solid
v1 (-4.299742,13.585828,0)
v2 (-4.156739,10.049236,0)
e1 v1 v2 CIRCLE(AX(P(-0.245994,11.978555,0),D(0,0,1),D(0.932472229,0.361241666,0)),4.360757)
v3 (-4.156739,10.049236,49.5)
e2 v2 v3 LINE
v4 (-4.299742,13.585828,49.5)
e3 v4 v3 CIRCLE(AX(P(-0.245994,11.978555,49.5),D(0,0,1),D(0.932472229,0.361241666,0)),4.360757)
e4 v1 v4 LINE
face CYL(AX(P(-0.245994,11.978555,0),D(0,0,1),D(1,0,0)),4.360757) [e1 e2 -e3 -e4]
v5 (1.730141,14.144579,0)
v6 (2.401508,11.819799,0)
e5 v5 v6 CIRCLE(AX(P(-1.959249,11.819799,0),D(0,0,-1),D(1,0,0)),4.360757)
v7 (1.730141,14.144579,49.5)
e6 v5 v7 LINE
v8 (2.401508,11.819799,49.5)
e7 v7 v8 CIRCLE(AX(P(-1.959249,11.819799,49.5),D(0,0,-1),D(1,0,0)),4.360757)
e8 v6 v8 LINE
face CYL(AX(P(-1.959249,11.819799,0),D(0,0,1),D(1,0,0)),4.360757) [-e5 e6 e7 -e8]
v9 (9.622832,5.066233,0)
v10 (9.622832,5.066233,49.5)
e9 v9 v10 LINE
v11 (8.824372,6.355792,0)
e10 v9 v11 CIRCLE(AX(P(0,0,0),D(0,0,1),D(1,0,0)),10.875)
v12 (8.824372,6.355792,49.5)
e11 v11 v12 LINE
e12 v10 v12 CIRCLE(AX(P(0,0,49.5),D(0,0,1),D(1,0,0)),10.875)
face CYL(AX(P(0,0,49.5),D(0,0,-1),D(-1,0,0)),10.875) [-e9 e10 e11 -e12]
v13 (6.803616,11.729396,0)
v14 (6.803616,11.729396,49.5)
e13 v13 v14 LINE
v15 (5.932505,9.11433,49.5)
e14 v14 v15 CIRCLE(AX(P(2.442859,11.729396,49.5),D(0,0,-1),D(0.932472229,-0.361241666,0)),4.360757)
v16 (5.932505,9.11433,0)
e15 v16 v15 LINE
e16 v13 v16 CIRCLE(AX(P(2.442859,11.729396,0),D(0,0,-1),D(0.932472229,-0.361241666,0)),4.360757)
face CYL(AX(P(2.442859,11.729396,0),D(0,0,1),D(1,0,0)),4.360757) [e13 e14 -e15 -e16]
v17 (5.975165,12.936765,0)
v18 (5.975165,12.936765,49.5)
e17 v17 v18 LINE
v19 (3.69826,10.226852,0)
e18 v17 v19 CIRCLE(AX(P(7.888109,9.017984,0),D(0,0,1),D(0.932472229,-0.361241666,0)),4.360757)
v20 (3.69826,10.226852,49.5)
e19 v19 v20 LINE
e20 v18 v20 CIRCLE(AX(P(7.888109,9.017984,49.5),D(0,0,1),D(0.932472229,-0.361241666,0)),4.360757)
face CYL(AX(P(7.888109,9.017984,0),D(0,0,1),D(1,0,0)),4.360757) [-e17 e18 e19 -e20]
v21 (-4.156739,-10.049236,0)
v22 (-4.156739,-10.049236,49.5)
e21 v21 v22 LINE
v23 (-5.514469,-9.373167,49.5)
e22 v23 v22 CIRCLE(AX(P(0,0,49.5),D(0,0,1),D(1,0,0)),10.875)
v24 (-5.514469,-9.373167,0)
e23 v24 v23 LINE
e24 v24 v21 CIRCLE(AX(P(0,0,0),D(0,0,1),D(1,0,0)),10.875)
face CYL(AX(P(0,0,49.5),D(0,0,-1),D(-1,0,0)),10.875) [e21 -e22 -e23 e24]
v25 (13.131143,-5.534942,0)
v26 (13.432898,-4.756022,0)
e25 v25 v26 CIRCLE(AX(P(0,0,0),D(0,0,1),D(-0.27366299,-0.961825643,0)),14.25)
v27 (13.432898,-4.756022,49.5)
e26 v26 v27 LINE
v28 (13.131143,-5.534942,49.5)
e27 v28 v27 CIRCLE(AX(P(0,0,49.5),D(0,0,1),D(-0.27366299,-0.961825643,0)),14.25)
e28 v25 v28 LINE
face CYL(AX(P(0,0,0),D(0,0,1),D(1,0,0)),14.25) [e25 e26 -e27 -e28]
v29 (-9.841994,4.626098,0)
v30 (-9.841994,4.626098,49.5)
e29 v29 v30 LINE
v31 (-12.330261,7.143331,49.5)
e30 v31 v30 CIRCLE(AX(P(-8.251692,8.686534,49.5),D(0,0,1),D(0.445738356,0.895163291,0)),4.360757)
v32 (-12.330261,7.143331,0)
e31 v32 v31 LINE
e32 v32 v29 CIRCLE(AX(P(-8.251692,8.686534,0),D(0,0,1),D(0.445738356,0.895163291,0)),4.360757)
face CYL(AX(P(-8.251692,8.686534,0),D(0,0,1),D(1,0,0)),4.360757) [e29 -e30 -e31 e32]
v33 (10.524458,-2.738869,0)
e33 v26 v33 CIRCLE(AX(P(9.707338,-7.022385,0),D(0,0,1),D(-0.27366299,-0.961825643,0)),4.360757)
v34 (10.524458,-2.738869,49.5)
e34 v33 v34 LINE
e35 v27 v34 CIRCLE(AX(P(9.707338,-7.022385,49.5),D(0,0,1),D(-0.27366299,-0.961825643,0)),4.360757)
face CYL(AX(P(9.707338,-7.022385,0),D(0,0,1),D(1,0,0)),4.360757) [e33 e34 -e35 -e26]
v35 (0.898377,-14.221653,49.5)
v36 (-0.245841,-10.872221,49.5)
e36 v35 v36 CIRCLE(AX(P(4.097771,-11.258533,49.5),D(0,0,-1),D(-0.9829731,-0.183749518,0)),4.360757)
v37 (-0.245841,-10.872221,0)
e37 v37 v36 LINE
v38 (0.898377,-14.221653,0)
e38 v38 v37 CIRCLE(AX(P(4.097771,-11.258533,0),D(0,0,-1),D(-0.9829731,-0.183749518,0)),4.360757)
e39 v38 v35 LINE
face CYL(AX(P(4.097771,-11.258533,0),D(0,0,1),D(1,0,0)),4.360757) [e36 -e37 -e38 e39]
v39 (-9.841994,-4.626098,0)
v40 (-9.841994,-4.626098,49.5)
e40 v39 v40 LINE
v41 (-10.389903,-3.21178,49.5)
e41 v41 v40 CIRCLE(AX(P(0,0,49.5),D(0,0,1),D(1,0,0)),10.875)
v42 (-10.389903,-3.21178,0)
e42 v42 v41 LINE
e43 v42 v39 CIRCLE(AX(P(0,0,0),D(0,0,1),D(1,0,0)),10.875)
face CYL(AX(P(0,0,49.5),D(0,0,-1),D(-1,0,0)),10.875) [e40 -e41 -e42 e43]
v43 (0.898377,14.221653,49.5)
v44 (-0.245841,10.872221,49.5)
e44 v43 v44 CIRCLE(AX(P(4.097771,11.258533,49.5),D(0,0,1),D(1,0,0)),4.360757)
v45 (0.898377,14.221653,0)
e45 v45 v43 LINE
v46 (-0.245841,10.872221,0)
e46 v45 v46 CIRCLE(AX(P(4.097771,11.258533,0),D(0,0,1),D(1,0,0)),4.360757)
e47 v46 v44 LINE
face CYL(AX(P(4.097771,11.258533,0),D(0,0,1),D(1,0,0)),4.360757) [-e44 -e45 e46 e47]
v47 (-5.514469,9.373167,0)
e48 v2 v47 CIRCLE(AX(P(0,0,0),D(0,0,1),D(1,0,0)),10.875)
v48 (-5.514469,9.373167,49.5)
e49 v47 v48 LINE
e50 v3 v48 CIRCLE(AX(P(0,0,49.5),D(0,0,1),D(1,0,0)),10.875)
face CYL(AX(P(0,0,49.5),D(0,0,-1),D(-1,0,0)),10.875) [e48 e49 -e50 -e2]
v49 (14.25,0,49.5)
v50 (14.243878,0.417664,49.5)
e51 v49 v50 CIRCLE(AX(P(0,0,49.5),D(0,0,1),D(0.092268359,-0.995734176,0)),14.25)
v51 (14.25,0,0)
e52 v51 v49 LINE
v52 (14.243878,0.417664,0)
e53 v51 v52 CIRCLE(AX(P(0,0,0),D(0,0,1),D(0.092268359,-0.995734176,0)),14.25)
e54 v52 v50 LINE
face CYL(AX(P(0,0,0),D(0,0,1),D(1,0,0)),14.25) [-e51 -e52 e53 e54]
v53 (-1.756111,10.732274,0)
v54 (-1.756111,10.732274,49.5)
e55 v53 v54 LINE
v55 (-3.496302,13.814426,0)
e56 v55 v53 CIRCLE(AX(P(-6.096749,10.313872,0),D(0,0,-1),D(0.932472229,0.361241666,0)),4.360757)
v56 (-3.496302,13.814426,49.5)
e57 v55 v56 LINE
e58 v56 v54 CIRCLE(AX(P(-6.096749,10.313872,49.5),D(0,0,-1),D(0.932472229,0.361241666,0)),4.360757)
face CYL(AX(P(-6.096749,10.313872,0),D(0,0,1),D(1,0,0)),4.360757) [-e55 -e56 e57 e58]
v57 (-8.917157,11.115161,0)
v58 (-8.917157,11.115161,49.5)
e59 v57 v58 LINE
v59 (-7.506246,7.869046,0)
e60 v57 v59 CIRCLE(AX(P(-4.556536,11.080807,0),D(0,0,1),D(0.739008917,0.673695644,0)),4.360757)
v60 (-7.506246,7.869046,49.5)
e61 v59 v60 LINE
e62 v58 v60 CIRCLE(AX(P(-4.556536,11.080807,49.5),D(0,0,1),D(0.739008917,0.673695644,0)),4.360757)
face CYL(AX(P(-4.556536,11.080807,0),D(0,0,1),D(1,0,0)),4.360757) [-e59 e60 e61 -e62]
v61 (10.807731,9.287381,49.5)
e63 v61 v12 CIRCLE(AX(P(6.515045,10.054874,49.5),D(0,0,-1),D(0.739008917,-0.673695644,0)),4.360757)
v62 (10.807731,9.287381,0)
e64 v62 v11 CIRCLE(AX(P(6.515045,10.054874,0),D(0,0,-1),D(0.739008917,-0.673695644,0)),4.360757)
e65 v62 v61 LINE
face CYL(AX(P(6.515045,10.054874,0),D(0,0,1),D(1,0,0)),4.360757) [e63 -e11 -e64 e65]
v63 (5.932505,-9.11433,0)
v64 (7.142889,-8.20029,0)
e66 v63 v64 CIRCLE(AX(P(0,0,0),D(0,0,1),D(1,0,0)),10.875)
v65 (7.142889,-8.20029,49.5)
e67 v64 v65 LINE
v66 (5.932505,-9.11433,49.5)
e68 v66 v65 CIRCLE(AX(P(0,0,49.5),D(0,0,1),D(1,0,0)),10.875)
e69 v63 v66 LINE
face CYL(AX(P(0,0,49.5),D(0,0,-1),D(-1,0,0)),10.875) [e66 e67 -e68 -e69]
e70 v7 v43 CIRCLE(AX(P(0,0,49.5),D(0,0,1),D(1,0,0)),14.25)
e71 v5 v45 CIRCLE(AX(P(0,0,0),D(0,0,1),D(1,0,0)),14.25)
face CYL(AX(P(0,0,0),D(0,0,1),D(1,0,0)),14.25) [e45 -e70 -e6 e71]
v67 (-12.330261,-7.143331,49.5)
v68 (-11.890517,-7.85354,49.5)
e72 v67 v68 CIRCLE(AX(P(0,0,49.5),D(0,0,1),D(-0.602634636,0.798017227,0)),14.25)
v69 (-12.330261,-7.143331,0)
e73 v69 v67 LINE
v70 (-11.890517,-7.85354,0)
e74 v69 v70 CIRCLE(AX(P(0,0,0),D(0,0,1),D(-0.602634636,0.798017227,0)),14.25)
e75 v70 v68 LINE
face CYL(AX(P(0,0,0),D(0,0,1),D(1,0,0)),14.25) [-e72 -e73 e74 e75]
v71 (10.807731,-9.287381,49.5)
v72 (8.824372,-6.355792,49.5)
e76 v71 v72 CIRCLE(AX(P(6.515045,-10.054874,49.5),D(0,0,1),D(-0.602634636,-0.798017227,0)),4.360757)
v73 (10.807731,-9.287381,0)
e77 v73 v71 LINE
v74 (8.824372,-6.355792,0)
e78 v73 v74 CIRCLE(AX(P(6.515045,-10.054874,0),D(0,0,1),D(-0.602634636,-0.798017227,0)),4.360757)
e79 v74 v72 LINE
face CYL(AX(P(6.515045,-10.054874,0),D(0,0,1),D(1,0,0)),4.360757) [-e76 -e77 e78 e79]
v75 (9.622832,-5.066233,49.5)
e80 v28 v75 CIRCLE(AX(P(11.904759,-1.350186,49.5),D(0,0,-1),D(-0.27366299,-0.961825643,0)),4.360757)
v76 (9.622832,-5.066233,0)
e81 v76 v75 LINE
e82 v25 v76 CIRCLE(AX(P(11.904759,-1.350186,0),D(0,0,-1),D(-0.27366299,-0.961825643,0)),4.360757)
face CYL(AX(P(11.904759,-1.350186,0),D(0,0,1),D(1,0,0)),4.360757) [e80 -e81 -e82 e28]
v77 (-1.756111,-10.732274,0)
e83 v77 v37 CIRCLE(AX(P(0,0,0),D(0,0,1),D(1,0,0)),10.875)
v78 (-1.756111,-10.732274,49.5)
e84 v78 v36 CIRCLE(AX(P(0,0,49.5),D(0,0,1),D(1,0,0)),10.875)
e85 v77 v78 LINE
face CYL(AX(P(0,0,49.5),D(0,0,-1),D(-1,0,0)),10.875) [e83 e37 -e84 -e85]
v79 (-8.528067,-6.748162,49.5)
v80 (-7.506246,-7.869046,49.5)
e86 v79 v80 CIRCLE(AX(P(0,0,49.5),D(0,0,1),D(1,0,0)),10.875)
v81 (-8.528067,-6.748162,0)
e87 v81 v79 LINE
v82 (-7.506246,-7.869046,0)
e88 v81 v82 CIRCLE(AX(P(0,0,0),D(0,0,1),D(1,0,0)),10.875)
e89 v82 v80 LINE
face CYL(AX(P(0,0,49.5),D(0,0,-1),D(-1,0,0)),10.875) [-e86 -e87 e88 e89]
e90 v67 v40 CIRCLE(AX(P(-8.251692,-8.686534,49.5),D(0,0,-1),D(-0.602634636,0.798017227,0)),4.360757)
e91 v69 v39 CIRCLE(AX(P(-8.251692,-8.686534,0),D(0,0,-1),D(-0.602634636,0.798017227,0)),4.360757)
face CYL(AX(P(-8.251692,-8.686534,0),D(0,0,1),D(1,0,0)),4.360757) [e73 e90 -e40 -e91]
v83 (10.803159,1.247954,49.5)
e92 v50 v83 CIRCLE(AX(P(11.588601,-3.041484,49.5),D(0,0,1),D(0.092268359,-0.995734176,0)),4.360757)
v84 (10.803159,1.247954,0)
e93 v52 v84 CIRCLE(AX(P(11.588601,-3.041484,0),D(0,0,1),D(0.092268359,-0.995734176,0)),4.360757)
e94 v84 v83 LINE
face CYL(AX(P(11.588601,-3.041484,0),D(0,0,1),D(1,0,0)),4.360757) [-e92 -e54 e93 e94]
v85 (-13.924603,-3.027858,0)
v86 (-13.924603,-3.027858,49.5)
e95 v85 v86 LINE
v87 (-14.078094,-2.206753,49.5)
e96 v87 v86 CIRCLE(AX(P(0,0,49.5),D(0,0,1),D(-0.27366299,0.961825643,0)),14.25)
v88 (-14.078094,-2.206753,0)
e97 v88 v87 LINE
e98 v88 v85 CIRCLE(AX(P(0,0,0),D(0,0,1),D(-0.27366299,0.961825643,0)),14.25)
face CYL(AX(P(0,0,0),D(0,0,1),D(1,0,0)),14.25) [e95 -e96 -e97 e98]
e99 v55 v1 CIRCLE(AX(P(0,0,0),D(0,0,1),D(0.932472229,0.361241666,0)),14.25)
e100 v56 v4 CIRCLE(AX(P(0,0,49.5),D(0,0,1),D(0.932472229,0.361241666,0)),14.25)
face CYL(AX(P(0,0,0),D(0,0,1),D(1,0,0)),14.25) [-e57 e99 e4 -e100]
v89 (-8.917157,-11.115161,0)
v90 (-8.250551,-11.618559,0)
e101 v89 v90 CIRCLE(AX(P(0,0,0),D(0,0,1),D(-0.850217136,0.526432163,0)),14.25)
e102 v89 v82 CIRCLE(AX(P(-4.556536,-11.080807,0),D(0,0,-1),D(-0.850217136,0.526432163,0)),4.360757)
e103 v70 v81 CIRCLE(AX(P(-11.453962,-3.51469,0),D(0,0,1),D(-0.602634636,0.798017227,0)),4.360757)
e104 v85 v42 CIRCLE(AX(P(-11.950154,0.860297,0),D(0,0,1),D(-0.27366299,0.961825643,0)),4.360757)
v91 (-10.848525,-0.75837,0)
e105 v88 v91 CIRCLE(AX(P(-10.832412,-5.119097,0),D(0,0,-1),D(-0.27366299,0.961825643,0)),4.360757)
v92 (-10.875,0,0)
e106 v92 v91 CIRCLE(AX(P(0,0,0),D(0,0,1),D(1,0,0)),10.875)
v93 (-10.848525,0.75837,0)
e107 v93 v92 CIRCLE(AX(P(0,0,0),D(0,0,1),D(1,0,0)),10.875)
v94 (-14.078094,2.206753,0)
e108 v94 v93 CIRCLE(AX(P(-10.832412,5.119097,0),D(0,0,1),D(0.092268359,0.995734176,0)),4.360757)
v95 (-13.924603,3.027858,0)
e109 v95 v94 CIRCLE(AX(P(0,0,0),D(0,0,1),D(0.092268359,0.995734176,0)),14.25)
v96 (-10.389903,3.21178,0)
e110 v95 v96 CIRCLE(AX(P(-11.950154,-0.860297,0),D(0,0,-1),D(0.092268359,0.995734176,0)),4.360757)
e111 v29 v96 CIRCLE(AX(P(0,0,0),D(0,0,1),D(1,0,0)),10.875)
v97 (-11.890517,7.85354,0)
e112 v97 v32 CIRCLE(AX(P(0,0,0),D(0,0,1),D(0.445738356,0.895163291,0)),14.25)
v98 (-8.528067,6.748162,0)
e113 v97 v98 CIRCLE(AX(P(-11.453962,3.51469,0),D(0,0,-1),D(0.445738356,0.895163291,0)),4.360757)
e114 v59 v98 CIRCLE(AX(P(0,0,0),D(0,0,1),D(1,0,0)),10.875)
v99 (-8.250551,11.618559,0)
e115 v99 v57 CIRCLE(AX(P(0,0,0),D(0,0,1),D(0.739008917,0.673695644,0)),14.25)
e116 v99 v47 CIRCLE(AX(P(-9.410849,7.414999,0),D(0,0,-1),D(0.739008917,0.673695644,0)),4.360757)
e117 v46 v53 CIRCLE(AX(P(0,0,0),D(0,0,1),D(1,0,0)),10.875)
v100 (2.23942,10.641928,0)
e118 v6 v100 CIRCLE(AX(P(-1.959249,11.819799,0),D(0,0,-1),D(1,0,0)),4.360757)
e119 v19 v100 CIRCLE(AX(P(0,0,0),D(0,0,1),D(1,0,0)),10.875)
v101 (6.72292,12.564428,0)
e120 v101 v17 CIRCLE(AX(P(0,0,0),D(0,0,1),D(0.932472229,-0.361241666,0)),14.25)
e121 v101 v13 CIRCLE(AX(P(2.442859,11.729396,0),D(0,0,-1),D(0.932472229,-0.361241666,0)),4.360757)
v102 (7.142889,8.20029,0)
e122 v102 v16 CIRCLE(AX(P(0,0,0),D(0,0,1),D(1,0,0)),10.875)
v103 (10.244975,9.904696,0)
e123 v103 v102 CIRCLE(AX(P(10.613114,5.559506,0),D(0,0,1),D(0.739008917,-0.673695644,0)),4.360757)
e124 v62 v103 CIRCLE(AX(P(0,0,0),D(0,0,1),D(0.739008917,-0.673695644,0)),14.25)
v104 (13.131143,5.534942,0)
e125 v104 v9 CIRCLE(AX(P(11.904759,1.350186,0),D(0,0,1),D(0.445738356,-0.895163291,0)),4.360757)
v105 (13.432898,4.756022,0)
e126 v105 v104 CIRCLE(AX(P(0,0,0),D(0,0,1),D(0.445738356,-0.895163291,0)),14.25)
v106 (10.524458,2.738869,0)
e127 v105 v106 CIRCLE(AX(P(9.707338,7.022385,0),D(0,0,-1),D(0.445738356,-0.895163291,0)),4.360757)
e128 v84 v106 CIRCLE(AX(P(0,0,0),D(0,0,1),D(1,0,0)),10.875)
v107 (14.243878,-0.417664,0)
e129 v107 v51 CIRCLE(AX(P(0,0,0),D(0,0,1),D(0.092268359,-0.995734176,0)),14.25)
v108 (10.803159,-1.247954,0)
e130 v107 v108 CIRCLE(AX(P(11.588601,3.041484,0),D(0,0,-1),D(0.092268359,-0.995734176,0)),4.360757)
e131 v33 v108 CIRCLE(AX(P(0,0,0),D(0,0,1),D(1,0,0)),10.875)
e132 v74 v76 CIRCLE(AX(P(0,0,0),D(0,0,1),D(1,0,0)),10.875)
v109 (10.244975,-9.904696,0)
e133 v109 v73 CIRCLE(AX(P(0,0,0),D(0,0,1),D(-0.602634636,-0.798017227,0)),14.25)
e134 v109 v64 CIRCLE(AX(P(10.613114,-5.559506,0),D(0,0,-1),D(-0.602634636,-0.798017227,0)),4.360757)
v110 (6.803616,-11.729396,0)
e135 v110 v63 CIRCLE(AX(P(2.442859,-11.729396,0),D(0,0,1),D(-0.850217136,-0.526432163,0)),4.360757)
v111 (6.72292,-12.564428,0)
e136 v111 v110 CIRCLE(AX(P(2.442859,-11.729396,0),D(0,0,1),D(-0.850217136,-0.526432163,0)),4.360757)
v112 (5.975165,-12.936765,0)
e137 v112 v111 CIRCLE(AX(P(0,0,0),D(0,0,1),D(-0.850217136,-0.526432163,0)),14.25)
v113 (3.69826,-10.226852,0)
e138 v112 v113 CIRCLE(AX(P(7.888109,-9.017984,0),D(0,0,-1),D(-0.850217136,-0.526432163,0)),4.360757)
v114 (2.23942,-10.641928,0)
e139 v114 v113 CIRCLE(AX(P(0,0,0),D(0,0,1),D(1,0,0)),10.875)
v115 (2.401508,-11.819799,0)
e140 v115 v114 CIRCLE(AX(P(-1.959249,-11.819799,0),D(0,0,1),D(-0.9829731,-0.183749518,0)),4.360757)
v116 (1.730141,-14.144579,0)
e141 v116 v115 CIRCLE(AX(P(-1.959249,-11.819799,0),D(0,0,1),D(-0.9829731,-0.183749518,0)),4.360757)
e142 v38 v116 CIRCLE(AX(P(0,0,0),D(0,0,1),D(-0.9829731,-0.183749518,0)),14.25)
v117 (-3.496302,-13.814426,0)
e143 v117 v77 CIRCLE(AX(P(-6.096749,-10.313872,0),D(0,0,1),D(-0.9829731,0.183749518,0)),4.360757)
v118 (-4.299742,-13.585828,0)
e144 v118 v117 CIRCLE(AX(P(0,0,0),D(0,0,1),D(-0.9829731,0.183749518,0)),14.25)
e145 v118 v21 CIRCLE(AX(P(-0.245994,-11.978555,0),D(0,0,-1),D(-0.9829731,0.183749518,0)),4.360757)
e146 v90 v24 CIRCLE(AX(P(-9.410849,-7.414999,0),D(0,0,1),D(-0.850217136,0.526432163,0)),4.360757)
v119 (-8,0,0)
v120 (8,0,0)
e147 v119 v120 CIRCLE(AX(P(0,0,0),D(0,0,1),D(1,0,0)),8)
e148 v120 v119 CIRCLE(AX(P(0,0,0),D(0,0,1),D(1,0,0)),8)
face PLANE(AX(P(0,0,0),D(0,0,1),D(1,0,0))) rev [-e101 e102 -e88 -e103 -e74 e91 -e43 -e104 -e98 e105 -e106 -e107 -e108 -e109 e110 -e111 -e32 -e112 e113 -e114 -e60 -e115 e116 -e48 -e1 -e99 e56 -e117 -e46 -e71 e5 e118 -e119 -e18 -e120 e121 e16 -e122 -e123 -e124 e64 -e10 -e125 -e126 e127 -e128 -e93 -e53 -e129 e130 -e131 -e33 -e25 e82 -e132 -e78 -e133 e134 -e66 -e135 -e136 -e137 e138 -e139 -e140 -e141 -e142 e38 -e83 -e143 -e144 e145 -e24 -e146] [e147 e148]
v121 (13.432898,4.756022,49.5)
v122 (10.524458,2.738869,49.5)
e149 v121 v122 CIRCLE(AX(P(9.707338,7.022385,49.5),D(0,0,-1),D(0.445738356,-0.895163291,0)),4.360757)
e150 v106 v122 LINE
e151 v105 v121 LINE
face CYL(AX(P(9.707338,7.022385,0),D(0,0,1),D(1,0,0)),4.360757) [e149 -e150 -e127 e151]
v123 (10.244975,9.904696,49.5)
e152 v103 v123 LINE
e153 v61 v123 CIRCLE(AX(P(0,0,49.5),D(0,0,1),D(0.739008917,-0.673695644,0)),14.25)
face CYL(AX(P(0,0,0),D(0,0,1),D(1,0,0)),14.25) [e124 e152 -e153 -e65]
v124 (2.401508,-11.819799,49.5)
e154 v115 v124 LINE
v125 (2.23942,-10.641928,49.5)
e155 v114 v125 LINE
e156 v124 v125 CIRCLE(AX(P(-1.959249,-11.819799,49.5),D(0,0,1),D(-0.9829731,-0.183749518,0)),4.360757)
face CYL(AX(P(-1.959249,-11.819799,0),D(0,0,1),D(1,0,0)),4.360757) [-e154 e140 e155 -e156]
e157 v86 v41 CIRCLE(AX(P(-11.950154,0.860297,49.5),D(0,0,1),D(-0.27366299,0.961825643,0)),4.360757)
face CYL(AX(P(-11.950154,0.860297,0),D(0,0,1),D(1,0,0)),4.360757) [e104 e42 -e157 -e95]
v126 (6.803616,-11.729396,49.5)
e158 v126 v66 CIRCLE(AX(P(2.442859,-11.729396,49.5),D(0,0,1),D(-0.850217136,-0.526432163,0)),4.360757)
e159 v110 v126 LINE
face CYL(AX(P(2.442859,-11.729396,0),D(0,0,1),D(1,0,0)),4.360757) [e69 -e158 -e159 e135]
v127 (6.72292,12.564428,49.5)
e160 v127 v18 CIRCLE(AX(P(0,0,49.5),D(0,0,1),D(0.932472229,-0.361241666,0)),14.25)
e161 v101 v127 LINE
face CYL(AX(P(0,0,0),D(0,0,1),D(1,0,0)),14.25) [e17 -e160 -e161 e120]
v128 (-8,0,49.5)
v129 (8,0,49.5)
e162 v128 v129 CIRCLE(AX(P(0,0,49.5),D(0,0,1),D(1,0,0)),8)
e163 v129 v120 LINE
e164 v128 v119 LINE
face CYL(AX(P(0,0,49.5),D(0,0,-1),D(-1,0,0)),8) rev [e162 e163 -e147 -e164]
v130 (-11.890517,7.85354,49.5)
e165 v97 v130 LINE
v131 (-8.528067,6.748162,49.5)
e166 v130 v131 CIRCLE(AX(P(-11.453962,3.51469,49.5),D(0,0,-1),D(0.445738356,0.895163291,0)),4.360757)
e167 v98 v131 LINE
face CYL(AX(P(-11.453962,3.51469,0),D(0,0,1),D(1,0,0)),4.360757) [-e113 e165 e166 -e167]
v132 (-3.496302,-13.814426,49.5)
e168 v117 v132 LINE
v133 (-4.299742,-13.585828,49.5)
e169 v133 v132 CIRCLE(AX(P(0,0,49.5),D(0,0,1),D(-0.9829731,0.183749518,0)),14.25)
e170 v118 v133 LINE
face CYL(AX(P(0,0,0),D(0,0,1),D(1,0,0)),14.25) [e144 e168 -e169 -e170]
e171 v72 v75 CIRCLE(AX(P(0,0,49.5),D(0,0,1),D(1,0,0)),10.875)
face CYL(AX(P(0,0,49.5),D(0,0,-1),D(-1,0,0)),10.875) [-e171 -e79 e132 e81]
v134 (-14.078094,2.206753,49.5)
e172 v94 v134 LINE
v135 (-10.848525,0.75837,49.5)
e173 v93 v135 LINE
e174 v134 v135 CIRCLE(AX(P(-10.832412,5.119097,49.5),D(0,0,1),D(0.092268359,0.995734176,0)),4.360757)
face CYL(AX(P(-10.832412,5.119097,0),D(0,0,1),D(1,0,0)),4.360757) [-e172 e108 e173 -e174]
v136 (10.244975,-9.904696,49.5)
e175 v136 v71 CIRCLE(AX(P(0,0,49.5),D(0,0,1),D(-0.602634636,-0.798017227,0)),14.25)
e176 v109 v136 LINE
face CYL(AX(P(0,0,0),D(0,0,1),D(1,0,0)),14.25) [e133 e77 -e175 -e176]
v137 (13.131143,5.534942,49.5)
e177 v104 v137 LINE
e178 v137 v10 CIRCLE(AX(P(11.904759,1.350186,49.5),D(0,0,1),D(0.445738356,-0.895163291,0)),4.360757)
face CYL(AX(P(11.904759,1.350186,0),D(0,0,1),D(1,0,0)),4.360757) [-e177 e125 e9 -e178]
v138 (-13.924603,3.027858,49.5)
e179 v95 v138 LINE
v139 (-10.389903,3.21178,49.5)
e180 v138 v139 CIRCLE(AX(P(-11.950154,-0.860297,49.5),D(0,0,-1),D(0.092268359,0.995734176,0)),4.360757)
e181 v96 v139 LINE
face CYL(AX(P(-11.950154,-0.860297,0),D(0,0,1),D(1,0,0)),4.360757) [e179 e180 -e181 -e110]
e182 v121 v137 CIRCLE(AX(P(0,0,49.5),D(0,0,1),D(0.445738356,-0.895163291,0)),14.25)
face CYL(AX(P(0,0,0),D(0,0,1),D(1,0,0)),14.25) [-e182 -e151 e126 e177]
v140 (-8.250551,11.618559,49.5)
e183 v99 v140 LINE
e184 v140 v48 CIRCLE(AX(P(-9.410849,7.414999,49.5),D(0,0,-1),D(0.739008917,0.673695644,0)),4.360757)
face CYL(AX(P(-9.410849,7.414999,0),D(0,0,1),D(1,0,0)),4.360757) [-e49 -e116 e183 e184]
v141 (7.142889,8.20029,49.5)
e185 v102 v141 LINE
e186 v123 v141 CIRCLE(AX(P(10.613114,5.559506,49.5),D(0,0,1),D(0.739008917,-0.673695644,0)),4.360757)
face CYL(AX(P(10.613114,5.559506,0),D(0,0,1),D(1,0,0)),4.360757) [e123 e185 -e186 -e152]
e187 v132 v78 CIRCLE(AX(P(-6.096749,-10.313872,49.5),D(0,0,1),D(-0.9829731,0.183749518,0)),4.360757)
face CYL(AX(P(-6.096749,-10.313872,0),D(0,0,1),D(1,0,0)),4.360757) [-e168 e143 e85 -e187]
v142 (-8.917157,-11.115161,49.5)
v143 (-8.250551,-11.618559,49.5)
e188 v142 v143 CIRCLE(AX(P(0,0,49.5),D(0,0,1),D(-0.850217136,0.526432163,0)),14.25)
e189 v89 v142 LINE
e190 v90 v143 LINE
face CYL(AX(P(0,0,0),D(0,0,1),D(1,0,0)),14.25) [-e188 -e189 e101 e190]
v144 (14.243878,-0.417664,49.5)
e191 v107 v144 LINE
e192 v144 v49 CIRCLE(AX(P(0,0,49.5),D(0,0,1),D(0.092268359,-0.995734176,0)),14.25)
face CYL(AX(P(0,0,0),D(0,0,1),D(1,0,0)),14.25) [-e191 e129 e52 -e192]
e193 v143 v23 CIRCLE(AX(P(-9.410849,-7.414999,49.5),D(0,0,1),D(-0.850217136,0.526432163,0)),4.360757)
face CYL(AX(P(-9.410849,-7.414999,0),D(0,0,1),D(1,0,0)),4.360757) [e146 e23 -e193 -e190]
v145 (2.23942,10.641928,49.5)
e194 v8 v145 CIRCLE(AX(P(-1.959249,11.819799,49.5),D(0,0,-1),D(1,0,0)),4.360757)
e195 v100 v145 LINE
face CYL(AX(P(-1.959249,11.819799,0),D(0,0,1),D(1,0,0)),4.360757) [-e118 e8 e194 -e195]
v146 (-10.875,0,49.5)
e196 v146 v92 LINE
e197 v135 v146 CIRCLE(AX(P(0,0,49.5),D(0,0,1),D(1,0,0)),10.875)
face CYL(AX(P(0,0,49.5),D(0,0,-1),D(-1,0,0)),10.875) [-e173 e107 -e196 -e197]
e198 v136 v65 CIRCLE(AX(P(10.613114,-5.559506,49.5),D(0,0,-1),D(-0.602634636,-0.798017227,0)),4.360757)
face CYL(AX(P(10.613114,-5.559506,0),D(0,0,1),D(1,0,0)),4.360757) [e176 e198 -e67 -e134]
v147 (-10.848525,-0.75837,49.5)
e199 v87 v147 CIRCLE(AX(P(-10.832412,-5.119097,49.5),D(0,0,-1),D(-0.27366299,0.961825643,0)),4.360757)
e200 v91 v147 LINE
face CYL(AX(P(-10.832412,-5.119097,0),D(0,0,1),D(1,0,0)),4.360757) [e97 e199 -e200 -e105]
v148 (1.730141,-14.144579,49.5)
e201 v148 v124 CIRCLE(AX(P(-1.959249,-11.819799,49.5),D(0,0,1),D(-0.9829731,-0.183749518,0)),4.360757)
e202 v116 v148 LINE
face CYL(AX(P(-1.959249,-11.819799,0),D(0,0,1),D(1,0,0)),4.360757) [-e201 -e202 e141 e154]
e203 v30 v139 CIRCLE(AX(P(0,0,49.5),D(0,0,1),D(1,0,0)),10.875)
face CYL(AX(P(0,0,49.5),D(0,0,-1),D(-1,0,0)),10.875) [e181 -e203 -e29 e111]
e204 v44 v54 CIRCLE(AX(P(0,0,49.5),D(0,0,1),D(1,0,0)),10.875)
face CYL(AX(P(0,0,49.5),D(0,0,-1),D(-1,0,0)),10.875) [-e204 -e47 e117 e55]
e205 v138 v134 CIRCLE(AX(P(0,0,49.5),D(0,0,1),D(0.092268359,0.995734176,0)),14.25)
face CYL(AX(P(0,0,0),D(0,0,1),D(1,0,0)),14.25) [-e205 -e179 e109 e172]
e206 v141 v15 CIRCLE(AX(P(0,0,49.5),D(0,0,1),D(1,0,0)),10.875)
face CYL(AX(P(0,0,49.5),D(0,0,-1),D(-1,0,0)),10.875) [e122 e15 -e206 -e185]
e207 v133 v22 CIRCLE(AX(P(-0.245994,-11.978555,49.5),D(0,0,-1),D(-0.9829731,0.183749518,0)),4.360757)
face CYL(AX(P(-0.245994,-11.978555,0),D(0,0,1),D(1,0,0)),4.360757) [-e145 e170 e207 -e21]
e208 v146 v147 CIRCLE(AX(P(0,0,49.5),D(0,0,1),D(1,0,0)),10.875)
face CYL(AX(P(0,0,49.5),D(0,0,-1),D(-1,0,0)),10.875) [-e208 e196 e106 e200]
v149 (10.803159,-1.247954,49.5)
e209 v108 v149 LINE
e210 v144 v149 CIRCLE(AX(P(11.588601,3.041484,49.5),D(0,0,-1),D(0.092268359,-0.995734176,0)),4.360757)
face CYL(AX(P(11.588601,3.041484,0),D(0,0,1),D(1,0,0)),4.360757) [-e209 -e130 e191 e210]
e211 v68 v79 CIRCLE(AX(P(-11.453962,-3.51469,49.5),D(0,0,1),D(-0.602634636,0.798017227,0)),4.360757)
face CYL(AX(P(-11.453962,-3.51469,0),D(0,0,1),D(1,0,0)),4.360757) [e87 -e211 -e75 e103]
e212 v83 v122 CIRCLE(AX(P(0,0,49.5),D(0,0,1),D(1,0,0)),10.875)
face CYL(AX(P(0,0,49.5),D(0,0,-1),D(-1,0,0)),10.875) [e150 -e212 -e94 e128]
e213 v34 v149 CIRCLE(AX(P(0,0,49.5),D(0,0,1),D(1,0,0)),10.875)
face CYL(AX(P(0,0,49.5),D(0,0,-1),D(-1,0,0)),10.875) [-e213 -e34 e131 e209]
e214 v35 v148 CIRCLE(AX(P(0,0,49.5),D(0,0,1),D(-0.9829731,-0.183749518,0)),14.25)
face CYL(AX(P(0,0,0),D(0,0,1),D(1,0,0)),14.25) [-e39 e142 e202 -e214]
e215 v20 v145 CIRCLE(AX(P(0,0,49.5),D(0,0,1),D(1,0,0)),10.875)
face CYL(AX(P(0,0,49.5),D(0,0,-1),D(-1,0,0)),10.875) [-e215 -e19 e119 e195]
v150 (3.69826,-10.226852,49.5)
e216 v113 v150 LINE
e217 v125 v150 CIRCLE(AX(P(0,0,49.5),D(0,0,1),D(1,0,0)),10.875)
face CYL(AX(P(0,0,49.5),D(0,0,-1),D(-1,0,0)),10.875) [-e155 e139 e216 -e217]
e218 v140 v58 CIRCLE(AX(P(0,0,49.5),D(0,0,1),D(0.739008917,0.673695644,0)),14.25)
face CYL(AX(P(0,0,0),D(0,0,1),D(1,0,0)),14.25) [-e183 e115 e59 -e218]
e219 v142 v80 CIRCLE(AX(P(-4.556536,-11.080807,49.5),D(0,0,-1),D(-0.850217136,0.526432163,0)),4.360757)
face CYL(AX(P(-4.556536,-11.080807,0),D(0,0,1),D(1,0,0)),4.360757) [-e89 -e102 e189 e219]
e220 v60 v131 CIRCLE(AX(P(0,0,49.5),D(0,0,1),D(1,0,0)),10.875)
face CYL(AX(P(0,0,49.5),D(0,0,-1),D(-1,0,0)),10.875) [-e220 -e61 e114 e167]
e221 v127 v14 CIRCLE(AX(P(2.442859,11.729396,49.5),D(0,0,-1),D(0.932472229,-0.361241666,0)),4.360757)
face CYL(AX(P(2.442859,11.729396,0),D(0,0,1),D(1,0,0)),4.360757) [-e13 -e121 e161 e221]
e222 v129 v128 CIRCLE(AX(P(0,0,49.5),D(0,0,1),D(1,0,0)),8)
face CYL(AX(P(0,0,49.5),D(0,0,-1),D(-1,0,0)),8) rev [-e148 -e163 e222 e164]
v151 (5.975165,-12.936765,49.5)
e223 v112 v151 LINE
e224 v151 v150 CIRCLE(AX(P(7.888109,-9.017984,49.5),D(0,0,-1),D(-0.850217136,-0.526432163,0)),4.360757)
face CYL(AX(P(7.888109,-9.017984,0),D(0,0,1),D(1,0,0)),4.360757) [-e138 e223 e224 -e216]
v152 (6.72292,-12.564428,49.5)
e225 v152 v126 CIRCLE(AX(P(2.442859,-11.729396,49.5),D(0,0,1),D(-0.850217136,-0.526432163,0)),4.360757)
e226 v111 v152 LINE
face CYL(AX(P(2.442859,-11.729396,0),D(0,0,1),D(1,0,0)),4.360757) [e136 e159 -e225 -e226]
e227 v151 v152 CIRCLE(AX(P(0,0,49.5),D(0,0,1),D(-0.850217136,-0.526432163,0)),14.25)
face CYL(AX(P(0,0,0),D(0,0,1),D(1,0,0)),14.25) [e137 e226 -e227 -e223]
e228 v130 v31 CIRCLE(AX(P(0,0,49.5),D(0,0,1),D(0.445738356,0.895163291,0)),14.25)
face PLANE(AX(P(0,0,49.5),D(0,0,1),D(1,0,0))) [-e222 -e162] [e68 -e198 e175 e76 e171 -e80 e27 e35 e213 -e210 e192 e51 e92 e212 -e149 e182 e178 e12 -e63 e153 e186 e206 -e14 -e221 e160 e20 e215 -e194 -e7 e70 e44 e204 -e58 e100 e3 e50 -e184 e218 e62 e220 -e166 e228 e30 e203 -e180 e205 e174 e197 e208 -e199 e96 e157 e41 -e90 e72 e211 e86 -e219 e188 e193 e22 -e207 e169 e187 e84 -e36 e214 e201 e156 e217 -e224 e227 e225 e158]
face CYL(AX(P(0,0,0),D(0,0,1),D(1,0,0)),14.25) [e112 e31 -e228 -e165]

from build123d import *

# Parameters (mm, degrees)
SKETCH1_R           = 10.875
SKETCH1_R_2         = 8
BOSS_EXTRUDE1_DEPTH = 49.5
BOSS_EXTRUDE2_START = -49.5
BOSS_EXTRUDE2_DEPTH = 49.5
CIRPATTERN1_COUNT   = 17


with BuildPart() as part:
    # Sketch1 → Boss-Extrude1 (new body)
    with BuildSketch(Plane.XY):
        Circle(SKETCH1_R)
        Circle(SKETCH1_R_2, mode=Mode.SUBTRACT)
    extrude(amount=BOSS_EXTRUDE1_DEPTH)

    # Sketch2 → Boss-Extrude2 (add)
    with BuildSketch(Plane.XY.offset(49.5).offset(BOSS_EXTRUDE2_START)):
        with BuildLine():
            ThreePointArc((2.239420157, 10.641927568), (2.356131909, 12.447246966), (1.730141322, 14.144578856))
            ThreePointArc((1.730141322, 14.144578856), (1.314824122, 14.189212012), (0.898377166, 14.221653155))
            ThreePointArc((0.898377166, 14.221653155), (-0.028838658, 12.668247034), (-0.245840713, 10.872220902))
            ThreePointArc((-0.245840713, 10.872220902), (1.003418409, 10.828609167), (2.239420157, 10.641927568))
        make_face()
    boss_extrude2 = extrude(amount=BOSS_EXTRUDE2_DEPTH)

    # CirPattern1: Boss-Extrude2 ×17 about axis
    cirpattern1_axis = Axis((0, 0, 0), (0, 0, 1))
    for i in range(1, CIRPATTERN1_COUNT):
        add(boss_extrude2.rotate(cirpattern1_axis, i * 360 / CIRPATTERN1_COUNT))


solid = part.part
